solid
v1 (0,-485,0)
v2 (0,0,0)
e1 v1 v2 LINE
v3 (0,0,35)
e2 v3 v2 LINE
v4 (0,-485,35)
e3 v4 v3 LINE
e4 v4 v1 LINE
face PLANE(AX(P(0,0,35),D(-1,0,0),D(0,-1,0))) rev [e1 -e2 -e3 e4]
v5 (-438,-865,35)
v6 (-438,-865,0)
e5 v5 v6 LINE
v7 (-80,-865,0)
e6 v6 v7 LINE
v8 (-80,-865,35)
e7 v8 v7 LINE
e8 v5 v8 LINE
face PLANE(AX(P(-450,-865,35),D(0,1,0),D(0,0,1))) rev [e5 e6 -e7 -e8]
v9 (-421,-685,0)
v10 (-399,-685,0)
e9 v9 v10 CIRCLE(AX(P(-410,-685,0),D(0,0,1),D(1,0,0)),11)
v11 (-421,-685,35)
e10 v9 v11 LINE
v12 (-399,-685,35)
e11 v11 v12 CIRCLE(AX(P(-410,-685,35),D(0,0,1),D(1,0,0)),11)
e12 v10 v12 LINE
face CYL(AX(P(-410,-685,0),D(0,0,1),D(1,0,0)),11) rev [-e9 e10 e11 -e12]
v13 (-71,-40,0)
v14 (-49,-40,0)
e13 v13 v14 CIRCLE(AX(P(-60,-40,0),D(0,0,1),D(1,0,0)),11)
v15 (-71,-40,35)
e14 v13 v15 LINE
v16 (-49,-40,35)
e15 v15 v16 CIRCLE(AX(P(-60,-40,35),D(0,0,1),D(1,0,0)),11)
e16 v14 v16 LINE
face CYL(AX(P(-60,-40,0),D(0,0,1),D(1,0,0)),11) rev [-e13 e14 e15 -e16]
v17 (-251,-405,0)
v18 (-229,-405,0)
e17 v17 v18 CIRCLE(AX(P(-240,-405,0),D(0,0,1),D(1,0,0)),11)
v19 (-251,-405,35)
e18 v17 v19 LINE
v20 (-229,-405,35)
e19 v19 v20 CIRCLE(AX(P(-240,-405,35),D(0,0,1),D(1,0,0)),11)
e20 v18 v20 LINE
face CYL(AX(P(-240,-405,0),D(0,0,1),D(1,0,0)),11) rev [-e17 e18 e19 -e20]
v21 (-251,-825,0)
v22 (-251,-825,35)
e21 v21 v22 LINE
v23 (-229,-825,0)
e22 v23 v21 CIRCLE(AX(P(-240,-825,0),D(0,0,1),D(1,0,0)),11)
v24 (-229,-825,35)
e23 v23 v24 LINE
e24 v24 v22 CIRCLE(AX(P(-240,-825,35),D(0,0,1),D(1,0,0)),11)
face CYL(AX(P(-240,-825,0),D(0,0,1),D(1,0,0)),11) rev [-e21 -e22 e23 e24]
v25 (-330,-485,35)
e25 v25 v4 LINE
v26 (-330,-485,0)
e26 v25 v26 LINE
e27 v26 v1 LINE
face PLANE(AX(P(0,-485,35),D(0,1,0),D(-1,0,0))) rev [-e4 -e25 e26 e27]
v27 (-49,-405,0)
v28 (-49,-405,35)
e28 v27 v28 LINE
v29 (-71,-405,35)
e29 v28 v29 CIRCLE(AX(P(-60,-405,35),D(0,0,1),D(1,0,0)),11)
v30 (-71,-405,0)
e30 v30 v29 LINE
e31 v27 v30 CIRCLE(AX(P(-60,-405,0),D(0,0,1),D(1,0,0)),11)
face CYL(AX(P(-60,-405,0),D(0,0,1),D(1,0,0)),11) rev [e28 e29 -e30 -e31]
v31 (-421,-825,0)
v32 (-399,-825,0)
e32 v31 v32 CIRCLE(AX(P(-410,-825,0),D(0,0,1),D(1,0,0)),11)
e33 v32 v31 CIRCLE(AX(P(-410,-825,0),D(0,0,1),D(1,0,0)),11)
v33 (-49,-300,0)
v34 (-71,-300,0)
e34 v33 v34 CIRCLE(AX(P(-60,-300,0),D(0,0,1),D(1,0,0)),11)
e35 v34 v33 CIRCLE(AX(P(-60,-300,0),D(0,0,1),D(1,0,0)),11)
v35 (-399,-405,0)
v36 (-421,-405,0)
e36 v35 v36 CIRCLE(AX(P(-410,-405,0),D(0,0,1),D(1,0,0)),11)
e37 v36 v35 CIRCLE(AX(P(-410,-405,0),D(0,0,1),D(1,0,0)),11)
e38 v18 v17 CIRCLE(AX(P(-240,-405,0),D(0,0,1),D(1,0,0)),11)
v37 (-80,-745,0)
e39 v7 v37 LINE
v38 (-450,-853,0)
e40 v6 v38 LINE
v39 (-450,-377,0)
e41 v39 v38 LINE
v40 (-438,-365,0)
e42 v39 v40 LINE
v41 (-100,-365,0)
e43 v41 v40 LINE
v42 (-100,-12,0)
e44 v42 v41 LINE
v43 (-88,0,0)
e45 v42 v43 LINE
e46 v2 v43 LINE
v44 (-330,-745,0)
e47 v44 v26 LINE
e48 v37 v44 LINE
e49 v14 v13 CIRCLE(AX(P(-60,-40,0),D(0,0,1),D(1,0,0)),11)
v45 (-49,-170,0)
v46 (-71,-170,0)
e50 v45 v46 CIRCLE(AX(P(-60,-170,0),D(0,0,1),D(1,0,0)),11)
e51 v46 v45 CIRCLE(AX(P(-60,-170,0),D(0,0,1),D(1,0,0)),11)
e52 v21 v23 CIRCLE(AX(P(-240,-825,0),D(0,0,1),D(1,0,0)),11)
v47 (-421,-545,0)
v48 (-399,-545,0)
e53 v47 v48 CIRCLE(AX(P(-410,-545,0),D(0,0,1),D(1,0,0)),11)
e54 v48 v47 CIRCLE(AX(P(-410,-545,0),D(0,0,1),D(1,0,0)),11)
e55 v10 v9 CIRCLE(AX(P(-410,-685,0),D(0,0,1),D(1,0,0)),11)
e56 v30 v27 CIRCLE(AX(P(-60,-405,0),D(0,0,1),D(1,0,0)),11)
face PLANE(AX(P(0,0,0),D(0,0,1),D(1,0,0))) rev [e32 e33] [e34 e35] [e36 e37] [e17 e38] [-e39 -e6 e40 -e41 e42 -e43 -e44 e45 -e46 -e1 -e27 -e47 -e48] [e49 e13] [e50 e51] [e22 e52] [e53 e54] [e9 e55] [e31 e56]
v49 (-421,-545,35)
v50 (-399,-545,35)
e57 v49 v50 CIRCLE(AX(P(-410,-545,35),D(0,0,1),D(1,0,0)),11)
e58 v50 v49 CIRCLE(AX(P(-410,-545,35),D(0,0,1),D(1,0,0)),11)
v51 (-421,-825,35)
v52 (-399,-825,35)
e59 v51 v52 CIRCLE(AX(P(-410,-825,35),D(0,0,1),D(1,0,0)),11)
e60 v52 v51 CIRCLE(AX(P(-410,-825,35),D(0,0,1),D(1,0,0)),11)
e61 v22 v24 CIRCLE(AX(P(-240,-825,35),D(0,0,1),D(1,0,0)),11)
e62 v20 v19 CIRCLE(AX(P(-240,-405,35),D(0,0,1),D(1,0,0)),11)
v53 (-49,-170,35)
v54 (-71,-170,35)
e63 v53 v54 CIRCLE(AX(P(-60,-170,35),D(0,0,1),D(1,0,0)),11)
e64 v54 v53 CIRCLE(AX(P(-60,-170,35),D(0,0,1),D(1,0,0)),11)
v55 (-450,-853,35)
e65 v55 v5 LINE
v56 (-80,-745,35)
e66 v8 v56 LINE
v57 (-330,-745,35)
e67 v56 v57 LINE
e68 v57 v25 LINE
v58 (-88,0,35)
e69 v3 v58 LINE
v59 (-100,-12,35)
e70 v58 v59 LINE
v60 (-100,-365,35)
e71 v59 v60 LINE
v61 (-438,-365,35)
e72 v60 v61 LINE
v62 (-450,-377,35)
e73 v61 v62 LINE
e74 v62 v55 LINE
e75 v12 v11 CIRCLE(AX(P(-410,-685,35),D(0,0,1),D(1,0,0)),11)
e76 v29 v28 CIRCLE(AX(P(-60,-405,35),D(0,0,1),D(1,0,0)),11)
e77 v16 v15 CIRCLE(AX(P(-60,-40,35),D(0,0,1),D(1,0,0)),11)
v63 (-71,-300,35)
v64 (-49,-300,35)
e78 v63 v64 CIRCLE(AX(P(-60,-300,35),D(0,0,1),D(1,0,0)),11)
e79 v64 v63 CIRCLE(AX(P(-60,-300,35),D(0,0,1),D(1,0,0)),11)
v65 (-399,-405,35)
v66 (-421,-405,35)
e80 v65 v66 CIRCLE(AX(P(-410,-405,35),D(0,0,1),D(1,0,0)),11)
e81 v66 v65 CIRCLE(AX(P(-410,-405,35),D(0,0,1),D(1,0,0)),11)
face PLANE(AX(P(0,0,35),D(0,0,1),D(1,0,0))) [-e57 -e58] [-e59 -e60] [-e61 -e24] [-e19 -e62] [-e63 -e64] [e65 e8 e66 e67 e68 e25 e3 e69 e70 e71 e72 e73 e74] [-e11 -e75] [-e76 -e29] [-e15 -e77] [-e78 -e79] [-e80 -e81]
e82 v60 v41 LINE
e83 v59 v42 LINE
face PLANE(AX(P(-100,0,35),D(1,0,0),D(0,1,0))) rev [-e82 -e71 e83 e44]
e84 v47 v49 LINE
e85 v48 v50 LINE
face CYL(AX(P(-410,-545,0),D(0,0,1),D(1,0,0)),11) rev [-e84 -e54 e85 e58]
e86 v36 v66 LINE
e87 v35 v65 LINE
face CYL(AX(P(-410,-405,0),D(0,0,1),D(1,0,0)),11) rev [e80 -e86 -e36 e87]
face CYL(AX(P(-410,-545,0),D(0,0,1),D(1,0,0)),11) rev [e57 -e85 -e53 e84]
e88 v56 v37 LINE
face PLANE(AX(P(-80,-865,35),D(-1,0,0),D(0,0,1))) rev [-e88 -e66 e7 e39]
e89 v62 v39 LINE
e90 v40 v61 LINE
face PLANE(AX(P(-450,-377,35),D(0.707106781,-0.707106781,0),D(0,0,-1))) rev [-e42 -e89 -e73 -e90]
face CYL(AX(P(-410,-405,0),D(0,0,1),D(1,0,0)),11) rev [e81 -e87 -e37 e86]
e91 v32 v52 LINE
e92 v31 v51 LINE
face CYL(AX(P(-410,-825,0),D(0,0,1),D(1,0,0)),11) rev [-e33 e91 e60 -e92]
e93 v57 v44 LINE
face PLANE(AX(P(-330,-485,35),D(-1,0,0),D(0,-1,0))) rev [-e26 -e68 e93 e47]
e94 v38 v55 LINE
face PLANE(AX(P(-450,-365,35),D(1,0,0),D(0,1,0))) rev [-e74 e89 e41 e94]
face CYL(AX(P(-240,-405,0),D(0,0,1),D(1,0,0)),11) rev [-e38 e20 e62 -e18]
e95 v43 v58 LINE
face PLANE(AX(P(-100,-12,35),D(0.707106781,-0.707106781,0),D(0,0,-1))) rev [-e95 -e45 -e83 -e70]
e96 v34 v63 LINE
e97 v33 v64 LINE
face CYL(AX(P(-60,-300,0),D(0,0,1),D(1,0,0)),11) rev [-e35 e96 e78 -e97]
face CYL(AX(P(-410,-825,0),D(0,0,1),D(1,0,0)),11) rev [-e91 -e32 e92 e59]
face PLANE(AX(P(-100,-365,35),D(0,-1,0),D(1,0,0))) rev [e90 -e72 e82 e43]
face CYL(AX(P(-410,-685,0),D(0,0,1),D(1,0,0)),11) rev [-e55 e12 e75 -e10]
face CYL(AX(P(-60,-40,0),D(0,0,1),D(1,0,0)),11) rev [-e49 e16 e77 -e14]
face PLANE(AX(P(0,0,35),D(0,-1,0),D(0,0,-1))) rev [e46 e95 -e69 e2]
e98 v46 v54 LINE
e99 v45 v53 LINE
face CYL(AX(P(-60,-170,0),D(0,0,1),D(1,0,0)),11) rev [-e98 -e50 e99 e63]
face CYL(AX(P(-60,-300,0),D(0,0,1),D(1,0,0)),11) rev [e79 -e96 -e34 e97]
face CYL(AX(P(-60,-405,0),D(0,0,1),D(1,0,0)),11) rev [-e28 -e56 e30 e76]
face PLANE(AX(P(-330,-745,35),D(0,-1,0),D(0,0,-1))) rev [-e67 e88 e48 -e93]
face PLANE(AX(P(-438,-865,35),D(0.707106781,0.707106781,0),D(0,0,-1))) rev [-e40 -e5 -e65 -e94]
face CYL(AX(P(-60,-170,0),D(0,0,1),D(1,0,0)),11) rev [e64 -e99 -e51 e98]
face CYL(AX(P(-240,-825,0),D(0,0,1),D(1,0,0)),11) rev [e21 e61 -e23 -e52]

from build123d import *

# Parameters (mm, degrees)
EXTRUDE_1_DEPTH          = 35
CHAMFER_1_SIZE           = 12
CUT_EXTRUDE_1_DEPTH      = 976.679250574
CUT_EXTRUDE_1_DEPTH_BACK = 976.679250574
SKETCH_2_R               = 11


with BuildPart() as part:
    # 草图1 → 凸台-拉伸1 (new body)
    with BuildSketch(Plane.XY):
        Polygon((0, 0), (0, -485), (-330, -485), (-330, -745), (-80, -745), (-80, -865), (-450, -865), (-450, -365), (-100, -365), (-100, 0), align=None)
    extrude(amount=EXTRUDE_1_DEPTH)

    # 倒角1
    chamfer_1_edges = [part.edges().sort_by_distance(p)[0] for p in [
        (-100, 0, 17.5),
        (-450, -865, 17.5),
        (-450, -365, 17.5),
    ]]
    chamfer(chamfer_1_edges, length=CHAMFER_1_SIZE)

    # 草图2 → 切除-拉伸1 (cut, two sides: drawn at the far end of the back side and taken through both)
    with BuildSketch(Plane.XY.offset(35).offset(-CUT_EXTRUDE_1_DEPTH_BACK)):
        with Locations((-60, -40)):
            Circle(SKETCH_2_R)
        with Locations((-60, -170)):
            Circle(SKETCH_2_R)
        with Locations((-60, -300)):
            Circle(SKETCH_2_R)
        with Locations((-60, -405)):
            Circle(SKETCH_2_R)
        with Locations((-240, -405)):
            Circle(SKETCH_2_R)
        with Locations((-410, -405)):
            Circle(SKETCH_2_R)
        with Locations((-410, -545)):
            Circle(SKETCH_2_R)
        with Locations((-410, -685)):
            Circle(SKETCH_2_R)
        with Locations((-410, -825)):
            Circle(SKETCH_2_R)
        with Locations((-240, -825)):
            Circle(SKETCH_2_R)
    extrude(amount=CUT_EXTRUDE_1_DEPTH + CUT_EXTRUDE_1_DEPTH_BACK, mode=Mode.SUBTRACT)


solid = part.part
